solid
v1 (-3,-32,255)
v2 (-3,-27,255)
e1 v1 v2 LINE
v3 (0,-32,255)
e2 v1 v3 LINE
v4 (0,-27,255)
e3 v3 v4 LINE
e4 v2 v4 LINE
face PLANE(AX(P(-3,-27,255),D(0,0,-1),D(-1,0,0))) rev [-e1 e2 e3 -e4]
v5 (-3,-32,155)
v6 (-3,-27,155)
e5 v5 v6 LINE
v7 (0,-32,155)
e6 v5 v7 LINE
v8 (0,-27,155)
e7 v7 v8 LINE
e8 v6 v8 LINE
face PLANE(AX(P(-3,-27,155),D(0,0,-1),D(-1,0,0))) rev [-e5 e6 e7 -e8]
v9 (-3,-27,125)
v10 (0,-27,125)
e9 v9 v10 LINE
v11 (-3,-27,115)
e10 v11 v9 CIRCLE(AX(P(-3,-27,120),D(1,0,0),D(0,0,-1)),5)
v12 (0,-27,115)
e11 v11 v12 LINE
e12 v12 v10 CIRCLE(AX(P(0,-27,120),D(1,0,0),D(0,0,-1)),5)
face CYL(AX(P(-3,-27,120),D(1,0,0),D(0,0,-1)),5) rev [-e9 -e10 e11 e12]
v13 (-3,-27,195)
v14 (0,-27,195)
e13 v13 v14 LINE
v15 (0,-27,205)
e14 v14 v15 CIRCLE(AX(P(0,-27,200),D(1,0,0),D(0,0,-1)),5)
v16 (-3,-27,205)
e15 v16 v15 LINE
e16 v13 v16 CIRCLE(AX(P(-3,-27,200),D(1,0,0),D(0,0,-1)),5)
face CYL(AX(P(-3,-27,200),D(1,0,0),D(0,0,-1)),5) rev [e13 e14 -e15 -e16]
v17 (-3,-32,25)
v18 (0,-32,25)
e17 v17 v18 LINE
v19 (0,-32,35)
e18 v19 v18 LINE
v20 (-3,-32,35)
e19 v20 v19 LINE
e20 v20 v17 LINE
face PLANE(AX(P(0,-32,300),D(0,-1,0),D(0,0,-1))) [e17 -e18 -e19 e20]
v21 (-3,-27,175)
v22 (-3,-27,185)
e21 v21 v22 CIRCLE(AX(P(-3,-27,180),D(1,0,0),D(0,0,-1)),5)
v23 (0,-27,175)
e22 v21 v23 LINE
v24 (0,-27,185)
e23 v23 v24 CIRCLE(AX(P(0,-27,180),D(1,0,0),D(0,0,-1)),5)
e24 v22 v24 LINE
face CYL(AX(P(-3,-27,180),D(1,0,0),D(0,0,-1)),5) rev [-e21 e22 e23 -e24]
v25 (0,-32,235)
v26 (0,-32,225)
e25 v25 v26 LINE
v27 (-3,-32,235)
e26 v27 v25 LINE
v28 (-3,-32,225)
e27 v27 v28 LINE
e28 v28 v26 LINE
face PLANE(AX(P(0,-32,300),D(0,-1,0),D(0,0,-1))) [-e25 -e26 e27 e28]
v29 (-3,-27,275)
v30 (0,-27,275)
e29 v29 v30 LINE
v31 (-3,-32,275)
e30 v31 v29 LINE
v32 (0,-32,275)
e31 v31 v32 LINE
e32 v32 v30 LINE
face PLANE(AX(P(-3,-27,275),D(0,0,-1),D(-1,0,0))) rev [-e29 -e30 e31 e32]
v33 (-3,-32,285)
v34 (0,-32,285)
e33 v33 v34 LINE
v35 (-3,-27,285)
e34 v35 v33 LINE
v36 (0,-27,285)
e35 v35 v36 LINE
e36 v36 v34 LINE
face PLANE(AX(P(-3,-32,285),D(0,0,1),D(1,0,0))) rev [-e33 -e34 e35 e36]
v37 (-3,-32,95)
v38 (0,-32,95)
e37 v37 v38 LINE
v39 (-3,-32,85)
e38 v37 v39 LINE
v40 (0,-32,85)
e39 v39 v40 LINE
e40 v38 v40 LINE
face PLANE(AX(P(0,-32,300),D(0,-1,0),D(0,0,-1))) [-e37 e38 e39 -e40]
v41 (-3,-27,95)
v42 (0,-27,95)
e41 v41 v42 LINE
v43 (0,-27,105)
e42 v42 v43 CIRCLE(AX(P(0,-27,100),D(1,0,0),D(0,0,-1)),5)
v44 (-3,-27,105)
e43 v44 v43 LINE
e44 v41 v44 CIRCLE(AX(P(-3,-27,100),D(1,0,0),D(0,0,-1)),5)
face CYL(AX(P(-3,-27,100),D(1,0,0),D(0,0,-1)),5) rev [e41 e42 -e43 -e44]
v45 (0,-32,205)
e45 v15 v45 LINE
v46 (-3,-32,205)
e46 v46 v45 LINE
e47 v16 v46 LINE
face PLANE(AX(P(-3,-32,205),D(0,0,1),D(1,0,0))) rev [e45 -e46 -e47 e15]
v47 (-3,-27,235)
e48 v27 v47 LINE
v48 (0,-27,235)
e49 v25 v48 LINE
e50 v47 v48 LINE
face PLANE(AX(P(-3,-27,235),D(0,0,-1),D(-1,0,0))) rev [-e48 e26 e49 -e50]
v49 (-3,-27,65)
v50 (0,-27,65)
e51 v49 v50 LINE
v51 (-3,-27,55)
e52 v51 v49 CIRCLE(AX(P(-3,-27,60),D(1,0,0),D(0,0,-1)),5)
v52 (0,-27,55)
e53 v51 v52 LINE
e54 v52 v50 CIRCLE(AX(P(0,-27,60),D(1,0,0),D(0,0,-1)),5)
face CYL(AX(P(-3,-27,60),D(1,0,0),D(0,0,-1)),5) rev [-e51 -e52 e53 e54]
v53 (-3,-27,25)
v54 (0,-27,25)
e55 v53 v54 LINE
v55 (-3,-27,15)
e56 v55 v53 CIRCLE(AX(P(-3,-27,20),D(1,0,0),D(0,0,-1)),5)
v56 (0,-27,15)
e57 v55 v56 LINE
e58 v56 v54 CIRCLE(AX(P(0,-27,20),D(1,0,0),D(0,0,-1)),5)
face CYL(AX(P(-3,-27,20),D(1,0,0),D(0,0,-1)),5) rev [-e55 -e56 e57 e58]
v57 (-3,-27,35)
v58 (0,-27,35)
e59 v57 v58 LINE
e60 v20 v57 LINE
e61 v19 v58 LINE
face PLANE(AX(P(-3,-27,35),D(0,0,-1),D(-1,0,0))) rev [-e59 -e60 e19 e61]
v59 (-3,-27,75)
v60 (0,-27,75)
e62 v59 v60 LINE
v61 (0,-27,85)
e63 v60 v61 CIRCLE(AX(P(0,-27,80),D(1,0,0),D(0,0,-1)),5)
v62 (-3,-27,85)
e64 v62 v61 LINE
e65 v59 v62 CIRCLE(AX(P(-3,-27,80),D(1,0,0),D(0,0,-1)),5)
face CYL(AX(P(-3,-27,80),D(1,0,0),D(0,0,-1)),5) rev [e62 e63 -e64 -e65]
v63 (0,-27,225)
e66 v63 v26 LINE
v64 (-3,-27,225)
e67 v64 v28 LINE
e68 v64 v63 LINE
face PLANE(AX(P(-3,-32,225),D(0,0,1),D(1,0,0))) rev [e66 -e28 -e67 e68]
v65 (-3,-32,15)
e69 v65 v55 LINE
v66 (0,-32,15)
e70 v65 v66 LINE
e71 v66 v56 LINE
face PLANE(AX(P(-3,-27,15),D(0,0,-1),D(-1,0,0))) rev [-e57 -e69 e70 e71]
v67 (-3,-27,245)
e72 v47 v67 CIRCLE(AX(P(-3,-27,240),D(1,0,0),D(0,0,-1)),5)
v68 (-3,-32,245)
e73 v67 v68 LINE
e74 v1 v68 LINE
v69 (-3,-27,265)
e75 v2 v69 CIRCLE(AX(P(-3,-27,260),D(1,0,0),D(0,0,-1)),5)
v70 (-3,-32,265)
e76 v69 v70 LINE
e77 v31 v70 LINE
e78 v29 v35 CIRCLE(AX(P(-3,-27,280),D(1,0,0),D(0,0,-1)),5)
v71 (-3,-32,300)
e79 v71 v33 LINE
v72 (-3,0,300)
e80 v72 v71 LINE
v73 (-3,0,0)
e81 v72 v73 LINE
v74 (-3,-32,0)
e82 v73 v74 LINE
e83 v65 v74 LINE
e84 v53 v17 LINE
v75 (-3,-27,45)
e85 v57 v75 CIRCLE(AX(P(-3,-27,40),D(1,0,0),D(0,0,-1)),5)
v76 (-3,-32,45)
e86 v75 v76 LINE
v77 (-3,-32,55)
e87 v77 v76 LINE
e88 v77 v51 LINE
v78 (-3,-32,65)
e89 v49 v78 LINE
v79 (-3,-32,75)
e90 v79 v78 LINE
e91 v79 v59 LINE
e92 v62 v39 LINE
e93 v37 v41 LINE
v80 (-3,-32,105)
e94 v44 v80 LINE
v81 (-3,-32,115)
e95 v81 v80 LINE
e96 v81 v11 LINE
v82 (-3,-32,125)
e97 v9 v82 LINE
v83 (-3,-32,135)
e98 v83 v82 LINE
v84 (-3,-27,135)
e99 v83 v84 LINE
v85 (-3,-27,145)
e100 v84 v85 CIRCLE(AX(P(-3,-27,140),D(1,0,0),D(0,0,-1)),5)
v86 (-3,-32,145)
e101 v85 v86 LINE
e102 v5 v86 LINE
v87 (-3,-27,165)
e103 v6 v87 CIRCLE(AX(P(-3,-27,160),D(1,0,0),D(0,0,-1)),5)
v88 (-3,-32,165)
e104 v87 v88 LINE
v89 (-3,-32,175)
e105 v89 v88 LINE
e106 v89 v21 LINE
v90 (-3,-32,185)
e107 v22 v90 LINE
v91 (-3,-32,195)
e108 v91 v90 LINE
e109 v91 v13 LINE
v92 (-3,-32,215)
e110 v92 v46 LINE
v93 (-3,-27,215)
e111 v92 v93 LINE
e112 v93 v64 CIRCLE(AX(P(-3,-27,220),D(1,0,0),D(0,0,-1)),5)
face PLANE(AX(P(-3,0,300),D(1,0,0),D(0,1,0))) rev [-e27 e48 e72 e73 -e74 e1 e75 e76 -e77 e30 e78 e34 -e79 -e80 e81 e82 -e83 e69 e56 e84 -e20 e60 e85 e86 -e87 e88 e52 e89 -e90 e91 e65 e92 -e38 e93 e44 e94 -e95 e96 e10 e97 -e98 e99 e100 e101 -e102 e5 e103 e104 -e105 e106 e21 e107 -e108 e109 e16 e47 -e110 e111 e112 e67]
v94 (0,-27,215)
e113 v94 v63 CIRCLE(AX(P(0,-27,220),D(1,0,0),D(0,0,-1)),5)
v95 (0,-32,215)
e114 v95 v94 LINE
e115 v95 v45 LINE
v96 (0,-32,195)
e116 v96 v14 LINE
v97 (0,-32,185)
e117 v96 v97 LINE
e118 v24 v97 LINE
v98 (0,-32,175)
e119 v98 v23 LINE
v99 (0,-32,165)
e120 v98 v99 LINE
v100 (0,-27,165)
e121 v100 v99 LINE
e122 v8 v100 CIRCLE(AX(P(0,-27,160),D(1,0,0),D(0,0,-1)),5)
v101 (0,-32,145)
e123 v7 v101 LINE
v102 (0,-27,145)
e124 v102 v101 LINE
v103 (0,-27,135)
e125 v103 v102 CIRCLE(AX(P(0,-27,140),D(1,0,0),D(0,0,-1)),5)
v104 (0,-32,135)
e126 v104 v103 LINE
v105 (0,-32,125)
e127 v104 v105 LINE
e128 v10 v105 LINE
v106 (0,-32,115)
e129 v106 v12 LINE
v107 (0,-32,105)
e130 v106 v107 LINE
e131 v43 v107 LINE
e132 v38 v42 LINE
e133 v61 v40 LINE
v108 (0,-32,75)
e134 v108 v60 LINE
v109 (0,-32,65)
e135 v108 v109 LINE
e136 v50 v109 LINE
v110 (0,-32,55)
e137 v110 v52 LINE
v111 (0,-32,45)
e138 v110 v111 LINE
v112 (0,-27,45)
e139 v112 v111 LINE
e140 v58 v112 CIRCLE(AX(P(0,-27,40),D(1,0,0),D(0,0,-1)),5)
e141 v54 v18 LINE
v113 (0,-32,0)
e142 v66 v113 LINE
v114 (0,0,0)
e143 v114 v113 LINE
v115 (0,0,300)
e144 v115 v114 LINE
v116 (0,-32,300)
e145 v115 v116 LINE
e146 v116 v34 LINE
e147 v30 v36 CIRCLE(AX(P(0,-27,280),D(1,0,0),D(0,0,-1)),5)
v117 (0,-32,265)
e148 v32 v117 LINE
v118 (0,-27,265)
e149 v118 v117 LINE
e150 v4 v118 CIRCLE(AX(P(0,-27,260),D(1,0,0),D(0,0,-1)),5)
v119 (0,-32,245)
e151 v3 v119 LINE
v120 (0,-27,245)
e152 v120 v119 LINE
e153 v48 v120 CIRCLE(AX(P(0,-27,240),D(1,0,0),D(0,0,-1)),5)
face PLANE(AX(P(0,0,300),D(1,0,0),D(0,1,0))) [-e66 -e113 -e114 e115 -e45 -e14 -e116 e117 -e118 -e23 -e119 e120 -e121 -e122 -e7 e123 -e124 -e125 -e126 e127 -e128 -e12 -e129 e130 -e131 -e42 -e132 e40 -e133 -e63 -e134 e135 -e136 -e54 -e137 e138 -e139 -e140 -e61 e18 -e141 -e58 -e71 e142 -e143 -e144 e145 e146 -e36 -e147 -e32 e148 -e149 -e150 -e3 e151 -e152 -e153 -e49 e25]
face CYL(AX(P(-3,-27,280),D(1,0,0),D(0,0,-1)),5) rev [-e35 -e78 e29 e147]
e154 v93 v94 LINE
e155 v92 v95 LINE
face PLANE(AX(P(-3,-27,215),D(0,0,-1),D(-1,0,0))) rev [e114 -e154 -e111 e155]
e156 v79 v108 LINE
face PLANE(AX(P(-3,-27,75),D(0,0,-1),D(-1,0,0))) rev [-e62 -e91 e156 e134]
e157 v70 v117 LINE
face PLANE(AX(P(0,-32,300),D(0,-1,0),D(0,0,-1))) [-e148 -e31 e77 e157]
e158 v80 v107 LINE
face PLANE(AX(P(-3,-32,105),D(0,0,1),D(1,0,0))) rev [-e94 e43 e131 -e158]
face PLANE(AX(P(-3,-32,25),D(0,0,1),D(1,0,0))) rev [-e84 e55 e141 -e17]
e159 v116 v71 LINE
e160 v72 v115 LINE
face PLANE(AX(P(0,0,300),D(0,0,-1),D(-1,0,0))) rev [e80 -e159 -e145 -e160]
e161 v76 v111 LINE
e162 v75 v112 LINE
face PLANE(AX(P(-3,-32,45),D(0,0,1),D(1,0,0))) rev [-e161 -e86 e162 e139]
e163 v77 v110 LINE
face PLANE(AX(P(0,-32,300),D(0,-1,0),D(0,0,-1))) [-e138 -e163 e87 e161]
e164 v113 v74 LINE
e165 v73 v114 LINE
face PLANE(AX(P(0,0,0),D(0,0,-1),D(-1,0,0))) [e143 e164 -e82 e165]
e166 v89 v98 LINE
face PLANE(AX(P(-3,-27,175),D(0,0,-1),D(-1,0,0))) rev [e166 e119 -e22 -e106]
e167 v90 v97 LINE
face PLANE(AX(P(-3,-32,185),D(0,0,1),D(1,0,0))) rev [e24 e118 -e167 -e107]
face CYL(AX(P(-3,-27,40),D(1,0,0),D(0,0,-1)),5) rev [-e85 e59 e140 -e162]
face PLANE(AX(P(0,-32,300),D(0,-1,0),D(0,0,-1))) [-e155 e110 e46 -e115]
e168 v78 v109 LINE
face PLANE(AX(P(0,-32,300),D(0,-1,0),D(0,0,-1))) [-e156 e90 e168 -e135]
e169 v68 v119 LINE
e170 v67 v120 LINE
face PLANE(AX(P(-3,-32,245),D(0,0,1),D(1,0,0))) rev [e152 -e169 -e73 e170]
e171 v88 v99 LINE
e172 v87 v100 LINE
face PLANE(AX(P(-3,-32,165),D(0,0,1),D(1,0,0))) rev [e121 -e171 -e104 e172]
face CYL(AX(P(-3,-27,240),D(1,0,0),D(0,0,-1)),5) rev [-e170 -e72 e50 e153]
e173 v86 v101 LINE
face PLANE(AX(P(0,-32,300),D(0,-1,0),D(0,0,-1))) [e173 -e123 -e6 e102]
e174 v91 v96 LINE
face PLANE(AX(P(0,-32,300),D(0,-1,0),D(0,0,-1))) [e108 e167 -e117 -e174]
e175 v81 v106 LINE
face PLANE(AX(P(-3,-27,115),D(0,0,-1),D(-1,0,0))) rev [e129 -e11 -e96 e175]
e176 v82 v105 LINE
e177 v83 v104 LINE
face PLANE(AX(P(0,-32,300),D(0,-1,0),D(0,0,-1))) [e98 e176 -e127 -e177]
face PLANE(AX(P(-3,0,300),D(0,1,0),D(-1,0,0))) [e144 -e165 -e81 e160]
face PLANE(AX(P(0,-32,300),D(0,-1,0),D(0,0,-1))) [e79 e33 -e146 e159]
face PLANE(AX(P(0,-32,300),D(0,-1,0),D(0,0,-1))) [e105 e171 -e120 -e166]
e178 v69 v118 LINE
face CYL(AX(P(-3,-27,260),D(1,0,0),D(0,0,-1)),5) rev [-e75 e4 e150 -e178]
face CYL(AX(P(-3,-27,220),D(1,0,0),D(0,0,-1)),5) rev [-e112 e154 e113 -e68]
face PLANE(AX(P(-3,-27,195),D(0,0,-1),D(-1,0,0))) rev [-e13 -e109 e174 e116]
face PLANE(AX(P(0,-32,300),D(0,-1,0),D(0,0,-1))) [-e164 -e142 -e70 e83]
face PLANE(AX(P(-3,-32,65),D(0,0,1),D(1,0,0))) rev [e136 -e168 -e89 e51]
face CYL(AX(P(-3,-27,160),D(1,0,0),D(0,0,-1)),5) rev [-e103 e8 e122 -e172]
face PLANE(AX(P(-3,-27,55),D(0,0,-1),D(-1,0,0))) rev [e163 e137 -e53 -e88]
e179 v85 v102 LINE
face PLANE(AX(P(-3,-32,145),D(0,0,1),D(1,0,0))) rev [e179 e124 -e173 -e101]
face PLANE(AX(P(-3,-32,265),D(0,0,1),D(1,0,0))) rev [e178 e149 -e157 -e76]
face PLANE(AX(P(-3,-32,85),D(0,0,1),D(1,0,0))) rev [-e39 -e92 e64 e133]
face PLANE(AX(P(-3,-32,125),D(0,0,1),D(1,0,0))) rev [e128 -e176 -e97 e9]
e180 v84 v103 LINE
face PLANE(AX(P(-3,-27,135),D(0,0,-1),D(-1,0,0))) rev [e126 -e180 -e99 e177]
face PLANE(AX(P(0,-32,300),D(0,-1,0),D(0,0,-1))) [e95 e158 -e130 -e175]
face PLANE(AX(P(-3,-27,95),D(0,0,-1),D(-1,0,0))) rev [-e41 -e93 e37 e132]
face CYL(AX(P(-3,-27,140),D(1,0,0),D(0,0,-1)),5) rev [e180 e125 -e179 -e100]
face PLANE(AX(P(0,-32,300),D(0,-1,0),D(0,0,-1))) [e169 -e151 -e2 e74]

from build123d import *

# Parameters (mm, degrees)
SKETCH1_W           = 3
SKETCH1_H           = 32
EXTRUDE_THIN1_DEPTH = 300
CUT_EXTRUDE1_DEPTH  = 302.716754589
LPATTERN1_COUNT     = 14
LPATTERN1_PITCH     = 20


with BuildPart() as part:
    # Sketch1 → Extrude-Thin1 (new body)
    with BuildSketch(Plane.XY):
        with Locations((-1.5, -16)):
            Rectangle(SKETCH1_W, SKETCH1_H)
    extrude(amount=EXTRUDE_THIN1_DEPTH)

    # Sketch2 → Cut-Extrude1 (cut, through all)
    with BuildSketch(Plane(origin=(0, 0, 0), x_dir=(0, 0, -1), z_dir=(1, 0, 0))):
        with BuildLine():
            Line((-275, -27), (-275, -32))
            Line((-275, -32), (-285, -32))
            Line((-285, -32), (-285, -27))
            ThreePointArc((-285, -27), (-280, -22), (-275, -27))
        make_face()
    cut_extrude1 = extrude(amount=-CUT_EXTRUDE1_DEPTH, mode=Mode.SUBTRACT)

    # LPattern1: Cut-Extrude1 ×14
    with Locations(*[(0, 0, -i * LPATTERN1_PITCH) for i in range(1, LPATTERN1_COUNT)]):
        add(cut_extrude1, mode=Mode.SUBTRACT)


solid = part.part
